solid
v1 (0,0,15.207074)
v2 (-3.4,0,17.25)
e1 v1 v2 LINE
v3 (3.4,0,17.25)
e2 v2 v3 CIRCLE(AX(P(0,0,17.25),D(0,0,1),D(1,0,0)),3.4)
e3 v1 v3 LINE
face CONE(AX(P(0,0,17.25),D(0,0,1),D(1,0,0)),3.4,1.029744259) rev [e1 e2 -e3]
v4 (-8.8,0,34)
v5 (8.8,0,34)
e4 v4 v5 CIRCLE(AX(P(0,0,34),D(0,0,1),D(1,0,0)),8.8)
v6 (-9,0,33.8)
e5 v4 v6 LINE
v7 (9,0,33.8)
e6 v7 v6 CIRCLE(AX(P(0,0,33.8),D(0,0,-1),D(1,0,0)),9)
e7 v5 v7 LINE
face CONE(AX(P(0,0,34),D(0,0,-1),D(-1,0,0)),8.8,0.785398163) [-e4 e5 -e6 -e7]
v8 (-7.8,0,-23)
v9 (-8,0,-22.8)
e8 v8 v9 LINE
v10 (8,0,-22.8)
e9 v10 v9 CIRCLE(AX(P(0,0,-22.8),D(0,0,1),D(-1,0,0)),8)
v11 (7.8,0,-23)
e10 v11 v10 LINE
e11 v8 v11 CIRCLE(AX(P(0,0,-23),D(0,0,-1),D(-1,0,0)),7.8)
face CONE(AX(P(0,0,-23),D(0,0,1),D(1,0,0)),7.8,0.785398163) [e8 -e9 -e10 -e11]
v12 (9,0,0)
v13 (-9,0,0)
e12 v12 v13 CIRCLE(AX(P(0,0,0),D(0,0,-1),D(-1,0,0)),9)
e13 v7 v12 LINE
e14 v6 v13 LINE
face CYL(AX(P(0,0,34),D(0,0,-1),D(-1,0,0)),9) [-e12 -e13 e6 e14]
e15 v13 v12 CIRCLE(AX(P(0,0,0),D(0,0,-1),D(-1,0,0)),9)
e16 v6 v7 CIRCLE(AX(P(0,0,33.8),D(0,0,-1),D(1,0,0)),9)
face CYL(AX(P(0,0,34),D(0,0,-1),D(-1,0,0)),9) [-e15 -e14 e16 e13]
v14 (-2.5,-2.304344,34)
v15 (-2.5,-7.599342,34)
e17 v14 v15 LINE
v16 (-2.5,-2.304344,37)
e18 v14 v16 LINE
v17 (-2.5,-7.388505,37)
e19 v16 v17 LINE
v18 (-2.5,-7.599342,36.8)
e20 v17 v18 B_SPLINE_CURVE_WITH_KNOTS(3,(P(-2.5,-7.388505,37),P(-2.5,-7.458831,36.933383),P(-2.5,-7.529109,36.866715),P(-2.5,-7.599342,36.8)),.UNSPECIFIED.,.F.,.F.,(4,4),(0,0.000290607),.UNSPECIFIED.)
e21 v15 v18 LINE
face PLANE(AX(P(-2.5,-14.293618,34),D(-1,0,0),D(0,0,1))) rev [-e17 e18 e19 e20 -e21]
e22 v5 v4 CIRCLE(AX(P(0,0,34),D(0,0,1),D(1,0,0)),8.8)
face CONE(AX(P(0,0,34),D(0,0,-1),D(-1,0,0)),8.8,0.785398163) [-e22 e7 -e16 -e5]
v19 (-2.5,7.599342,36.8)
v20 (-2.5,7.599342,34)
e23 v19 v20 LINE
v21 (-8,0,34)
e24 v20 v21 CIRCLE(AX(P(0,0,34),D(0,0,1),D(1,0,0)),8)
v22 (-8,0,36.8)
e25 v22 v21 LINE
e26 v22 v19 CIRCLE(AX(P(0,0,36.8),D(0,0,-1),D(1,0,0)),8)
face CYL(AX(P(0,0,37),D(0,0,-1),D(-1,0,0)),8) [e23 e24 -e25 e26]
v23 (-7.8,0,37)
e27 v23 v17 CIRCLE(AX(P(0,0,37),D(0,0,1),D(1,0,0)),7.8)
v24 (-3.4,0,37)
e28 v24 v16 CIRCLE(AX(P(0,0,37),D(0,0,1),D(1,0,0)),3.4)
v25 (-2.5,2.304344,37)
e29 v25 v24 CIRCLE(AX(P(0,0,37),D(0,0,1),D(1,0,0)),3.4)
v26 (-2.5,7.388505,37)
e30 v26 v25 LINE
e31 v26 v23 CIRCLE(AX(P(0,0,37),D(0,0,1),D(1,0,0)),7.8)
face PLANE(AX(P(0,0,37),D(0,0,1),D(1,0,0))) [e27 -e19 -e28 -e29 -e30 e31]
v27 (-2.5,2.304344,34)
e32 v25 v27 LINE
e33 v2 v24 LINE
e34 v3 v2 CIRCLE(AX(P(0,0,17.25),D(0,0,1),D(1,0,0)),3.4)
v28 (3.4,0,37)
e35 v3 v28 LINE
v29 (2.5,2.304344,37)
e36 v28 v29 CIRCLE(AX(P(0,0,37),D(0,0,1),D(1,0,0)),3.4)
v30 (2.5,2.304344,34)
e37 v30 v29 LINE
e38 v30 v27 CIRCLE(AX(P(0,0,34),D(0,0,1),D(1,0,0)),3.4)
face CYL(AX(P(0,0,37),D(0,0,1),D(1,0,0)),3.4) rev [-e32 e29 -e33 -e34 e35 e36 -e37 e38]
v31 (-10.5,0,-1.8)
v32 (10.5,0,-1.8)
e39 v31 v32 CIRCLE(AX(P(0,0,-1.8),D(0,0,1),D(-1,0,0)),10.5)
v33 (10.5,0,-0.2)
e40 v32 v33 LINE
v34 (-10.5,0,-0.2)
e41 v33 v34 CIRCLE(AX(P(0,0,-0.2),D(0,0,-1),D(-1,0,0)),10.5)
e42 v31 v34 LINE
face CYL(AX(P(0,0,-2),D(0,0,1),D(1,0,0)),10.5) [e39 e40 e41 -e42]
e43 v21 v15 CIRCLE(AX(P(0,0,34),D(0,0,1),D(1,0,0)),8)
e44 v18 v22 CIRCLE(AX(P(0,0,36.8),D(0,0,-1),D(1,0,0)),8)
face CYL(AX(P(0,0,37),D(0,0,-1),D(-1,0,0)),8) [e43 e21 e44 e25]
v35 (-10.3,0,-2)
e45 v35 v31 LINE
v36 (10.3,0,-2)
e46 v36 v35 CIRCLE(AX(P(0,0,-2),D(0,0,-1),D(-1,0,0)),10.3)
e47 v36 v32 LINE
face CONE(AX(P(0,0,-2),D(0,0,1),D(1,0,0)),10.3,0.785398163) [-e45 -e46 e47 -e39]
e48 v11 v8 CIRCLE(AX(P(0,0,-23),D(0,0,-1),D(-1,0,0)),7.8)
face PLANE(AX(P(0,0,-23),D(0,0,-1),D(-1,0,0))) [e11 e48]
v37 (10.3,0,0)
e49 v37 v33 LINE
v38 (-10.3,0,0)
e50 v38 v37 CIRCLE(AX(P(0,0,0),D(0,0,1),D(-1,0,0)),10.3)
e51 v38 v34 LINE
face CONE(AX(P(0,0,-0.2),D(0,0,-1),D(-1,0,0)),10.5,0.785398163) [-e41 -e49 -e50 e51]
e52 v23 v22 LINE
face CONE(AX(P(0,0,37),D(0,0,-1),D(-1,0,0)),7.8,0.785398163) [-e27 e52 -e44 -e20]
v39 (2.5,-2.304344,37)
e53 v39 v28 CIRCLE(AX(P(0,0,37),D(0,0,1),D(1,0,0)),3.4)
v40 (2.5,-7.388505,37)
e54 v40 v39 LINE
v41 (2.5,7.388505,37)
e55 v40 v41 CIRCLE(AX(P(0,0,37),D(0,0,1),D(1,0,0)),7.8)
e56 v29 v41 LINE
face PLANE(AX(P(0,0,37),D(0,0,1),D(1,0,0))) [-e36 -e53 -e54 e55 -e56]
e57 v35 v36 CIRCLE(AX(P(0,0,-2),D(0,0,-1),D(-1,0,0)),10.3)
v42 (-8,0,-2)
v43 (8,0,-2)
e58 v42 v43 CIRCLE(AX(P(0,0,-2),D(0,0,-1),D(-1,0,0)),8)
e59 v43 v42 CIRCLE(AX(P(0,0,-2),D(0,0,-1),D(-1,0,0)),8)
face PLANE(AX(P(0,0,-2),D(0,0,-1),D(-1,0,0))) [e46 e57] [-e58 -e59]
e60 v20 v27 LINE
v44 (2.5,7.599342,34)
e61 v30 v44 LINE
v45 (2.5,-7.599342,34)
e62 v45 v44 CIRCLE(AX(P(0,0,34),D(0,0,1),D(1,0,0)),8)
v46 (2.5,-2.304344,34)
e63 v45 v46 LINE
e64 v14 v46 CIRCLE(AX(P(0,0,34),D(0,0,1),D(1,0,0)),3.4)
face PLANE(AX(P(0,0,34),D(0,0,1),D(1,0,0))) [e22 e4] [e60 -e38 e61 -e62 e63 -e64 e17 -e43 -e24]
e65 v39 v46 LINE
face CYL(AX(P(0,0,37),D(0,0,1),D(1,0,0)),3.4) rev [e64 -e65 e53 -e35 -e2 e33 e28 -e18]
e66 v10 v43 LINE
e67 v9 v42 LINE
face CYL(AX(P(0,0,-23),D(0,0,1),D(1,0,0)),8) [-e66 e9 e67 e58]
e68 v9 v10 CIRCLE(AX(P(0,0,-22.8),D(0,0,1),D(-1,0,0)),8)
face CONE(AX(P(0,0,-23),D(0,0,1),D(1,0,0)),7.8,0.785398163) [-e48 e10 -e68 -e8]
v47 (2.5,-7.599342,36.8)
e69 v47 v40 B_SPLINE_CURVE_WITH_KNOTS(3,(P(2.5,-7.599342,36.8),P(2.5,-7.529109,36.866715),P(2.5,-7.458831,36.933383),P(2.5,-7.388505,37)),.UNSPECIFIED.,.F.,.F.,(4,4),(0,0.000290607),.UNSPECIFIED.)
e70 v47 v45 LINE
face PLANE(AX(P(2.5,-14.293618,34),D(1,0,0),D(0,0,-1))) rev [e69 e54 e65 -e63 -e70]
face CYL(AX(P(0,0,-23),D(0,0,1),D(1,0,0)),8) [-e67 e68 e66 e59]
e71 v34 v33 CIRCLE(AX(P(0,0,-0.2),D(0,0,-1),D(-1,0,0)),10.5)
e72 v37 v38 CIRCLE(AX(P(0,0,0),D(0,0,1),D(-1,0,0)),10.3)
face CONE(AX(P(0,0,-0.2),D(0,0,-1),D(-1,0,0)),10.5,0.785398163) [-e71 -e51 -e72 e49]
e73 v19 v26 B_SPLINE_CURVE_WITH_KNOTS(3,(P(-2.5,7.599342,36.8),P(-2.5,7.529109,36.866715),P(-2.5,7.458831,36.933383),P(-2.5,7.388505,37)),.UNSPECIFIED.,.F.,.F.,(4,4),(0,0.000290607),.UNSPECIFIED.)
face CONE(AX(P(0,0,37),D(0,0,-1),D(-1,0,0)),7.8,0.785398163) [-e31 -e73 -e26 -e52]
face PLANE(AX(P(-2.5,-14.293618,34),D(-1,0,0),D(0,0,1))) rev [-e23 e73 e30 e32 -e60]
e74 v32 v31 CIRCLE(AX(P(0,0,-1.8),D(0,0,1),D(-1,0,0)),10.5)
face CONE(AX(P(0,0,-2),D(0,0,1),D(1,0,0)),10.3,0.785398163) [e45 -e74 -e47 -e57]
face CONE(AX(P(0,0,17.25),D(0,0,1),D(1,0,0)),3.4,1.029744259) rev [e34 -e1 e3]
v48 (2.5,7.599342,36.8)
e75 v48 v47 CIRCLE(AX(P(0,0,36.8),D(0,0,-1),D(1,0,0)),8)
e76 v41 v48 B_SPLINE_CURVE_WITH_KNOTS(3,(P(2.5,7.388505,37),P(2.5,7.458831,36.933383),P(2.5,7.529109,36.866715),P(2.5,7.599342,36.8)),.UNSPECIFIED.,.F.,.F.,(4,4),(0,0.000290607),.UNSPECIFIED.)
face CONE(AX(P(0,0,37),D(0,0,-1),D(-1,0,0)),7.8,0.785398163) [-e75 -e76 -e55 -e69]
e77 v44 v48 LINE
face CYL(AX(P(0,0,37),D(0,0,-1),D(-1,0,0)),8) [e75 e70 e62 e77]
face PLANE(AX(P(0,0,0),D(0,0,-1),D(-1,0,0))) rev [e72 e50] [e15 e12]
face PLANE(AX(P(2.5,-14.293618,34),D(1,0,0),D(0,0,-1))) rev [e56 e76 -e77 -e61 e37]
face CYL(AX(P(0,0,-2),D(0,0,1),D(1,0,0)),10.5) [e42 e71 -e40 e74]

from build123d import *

# Parameters (mm, degrees)
SKETCH_1_R             = 9
EXTRUDE_1_DEPTH        = 34
SKETCH_2_R             = 8
EXTRUDE_2_DEPTH        = 3
SKETCH_3_R             = 10.5
EXTRUDE_3_DEPTH        = 2
EXTRUDE_START          = 21
SKETCH_4_R             = 8
EXTRUDE_4_DEPTH        = 21
SKETCH_5_W             = 5
SKETCH_5_H             = 32.45039325
CUT_EXTRUDE_1_DEPTH    = 3
HOLE_WIZARD_M8_1_D     = 6.8
HOLE_WIZARD_M8_1_DEPTH = 19.75
HOLE_WIZARD_M8_1_TIP   = 2.042926105
CHAMFER_1_SIZE         = 0.2


with BuildPart() as part:
    # 草图1 → 凸台-拉伸1 (new body)
    with BuildSketch(Plane.XY):
        Circle(SKETCH_1_R)
    extrude(amount=EXTRUDE_1_DEPTH)

    # 草图2 → 凸台-拉伸2 (add)
    with BuildSketch(Plane.XY.offset(34)):
        Circle(SKETCH_2_R)
    extrude(amount=EXTRUDE_2_DEPTH)

    # 草图3 → 凸台-拉伸3 (add)
    with BuildSketch(Plane(origin=(0, 0, 0), x_dir=(-1, 0, 0), z_dir=(0, 0, -1))):
        Circle(SKETCH_3_R)
    extrude(amount=EXTRUDE_3_DEPTH)

    # 草图4 → 凸台-拉伸4 (add)
    with BuildSketch(Plane(origin=(0, 0, -2), x_dir=(-1, 0, 0), z_dir=(0, 0, -1)).offset(EXTRUDE_START)):
        with Locations(Location((0, 0, 0), (0, 0, 180))):
            Circle(SKETCH_4_R)
    extrude(amount=-EXTRUDE_4_DEPTH)

    # 草图5 → 切除-拉伸1 (cut)
    with BuildSketch(Plane.XY.offset(37)):
        with Locations((0, 1.931578492)):
            Rectangle(SKETCH_5_W, SKETCH_5_H)
    extrude(amount=-CUT_EXTRUDE_1_DEPTH, mode=Mode.SUBTRACT)

    # M8 螺纹孔1
    with Locations(Plane.XY.offset(37)):
        with Locations((0, 0)):
            Hole(HOLE_WIZARD_M8_1_D / 2, depth=HOLE_WIZARD_M8_1_DEPTH)
            with Locations((0, 0, -(HOLE_WIZARD_M8_1_DEPTH + HOLE_WIZARD_M8_1_TIP / 2))):  # 118° drill point
                Cone(0, HOLE_WIZARD_M8_1_D / 2, HOLE_WIZARD_M8_1_TIP, mode=Mode.SUBTRACT)

    # 倒角1
    chamfer_1_edges = [part.edges().sort_by_distance(p)[0] for p in [
        (10.5, 0, -2),
        (-8, 0, -23),
        (-9, 0, 34),
        (-8, 0, 37),
        (8, 0, 37),
        (10.5, 0, 0),
    ]]
    chamfer(chamfer_1_edges, length=CHAMFER_1_SIZE)


solid = part.part
